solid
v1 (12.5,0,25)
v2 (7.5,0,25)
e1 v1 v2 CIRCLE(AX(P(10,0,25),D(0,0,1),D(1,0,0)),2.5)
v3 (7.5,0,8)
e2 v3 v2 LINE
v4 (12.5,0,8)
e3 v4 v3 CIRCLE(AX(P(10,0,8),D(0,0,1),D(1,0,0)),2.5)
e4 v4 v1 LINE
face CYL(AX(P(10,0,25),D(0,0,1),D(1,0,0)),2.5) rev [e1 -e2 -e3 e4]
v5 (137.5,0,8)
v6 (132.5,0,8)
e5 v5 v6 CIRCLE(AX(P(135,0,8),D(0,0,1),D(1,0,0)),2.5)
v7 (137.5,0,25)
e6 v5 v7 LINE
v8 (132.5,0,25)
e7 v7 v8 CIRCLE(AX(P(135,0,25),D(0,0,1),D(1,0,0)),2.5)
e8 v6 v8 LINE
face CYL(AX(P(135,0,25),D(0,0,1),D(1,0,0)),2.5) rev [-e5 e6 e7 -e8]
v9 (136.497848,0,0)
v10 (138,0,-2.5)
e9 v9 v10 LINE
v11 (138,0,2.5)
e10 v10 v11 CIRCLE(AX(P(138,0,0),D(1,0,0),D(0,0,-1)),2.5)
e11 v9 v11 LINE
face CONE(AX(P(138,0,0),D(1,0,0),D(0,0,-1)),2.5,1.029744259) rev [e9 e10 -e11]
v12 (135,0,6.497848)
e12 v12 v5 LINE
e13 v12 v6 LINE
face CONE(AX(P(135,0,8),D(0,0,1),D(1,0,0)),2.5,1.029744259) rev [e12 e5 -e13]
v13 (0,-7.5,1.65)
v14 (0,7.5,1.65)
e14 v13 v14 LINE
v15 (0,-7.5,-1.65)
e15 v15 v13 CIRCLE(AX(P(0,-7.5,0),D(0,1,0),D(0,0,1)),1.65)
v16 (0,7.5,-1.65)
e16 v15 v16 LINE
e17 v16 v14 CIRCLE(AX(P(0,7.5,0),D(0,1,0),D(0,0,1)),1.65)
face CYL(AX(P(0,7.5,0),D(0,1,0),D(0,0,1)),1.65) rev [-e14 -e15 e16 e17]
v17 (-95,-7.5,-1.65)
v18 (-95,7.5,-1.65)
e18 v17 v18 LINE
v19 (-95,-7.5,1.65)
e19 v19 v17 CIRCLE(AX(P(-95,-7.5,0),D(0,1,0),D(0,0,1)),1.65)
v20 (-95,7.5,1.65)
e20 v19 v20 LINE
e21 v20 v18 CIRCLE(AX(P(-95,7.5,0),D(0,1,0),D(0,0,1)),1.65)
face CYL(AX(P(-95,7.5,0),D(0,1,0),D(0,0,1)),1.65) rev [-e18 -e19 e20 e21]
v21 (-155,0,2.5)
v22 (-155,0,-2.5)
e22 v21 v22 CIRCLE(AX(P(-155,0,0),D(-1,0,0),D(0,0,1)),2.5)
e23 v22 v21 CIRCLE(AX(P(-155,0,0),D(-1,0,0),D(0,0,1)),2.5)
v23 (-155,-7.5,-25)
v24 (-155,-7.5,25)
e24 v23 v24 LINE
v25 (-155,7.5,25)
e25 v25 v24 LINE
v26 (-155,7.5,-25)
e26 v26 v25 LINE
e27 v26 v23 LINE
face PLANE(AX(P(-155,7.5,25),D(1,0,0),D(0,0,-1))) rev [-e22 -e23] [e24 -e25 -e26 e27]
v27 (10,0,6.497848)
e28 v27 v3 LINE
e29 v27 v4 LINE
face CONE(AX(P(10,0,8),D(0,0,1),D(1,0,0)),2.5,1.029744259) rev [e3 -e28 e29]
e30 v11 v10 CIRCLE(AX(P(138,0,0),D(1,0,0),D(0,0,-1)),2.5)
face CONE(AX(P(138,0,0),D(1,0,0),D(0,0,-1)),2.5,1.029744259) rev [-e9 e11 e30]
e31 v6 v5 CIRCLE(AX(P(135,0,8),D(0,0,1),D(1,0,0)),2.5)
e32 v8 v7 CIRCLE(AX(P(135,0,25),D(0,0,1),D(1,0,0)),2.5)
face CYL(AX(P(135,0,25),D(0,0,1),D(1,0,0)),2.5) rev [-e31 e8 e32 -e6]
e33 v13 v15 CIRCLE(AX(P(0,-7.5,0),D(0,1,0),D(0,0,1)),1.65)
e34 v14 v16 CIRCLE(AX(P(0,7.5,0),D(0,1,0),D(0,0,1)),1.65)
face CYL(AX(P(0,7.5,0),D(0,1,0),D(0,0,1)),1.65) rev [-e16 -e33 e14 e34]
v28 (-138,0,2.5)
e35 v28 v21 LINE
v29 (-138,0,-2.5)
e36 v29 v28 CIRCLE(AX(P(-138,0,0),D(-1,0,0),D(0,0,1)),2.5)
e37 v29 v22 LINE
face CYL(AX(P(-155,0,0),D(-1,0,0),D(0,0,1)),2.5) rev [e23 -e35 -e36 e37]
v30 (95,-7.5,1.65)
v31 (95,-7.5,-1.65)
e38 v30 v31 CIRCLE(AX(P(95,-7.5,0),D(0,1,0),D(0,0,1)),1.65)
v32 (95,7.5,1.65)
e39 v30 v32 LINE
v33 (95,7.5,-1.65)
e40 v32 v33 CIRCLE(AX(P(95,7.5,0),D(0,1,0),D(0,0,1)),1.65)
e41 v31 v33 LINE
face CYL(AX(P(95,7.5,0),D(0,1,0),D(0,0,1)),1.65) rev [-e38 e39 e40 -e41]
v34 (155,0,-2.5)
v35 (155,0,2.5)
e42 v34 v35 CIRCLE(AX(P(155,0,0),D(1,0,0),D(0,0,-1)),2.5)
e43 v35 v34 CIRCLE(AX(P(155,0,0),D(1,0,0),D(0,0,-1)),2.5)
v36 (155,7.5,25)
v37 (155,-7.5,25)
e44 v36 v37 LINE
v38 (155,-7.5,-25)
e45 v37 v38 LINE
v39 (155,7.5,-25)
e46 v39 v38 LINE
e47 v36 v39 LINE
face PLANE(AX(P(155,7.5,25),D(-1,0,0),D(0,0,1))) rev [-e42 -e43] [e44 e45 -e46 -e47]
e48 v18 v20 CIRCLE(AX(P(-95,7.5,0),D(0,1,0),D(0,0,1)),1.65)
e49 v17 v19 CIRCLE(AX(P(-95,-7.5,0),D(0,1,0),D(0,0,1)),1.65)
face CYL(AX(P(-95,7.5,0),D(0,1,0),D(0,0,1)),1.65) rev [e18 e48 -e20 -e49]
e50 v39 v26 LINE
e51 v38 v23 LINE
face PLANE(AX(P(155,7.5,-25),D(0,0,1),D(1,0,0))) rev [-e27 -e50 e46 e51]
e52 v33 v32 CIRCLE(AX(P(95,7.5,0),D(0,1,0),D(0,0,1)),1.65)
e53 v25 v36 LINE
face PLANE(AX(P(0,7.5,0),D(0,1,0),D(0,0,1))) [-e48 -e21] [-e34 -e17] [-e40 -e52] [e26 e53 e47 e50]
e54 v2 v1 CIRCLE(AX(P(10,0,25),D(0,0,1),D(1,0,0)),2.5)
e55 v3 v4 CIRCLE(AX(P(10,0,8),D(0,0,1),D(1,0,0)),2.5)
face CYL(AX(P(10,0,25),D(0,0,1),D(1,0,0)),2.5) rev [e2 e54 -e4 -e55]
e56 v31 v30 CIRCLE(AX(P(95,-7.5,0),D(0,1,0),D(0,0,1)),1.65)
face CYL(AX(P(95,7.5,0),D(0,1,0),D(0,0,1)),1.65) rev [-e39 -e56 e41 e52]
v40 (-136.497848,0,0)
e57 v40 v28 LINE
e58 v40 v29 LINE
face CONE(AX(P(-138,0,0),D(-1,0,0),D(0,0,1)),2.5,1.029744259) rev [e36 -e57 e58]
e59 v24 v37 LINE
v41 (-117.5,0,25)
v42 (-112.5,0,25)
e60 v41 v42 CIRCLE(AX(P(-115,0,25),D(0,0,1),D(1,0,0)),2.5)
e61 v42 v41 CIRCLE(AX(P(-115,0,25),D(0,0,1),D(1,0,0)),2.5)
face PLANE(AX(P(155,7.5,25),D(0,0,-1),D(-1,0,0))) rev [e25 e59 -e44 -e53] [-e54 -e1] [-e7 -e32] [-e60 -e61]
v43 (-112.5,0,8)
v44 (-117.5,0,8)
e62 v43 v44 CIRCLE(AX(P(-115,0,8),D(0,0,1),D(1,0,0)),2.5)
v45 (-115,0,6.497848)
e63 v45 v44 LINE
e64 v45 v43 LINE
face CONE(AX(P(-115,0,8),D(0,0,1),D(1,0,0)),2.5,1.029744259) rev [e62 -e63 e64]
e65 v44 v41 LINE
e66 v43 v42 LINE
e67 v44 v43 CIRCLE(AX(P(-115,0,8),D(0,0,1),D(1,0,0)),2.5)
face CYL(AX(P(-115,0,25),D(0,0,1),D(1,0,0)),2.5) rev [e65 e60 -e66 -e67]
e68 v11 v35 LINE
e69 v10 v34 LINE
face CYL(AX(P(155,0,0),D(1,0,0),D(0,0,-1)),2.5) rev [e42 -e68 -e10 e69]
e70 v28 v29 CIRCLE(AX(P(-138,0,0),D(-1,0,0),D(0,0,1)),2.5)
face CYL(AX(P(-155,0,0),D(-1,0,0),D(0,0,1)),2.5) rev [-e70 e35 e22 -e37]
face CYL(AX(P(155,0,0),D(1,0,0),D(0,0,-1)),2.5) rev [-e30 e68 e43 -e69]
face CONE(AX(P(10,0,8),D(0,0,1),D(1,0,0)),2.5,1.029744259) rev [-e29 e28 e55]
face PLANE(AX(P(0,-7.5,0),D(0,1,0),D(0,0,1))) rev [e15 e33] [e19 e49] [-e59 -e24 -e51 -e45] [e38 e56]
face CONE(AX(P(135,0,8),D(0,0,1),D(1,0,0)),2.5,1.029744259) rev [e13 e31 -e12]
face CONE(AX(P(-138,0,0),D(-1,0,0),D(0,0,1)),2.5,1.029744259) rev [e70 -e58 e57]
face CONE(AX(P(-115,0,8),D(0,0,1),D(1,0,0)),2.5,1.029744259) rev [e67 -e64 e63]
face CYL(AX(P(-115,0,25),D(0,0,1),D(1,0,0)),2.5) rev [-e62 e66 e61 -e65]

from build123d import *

# Parameters (mm, degrees)
SKETCH_1_W             = 310
SKETCH_1_H             = 50
EXTRUDE_1_DEPTH        = 7.5
HOLE_WIZARD_M6_1_D     = 5
HOLE_WIZARD_M6_1_DEPTH = 17
HOLE_WIZARD_M6_1_TIP   = 1.502151548
HOLE_WIZARD_M6_2_D     = 5
HOLE_WIZARD_M6_2_DEPTH = 17
HOLE_WIZARD_M6_2_TIP   = 1.502151548
HOLE_WIZARD_M6_3_D     = 5
HOLE_WIZARD_M6_3_DEPTH = 17
HOLE_WIZARD_M6_3_TIP   = 1.502151548
HOLE_WIZARD_M4_1_D     = 3.3


with BuildPart() as part:
    # 草图1 → 凸台-拉伸1 (new, symmetric)
    with BuildSketch(Plane(origin=(0, 0, 0), x_dir=(1, 0, 0), z_dir=(0, 1, 0))):
        Rectangle(SKETCH_1_W, SKETCH_1_H)
    extrude(amount=EXTRUDE_1_DEPTH, both=True)

    # M6 螺纹孔1
    with Locations(Plane.XY.offset(25)):
        with Locations((-115, 0), (10, 0), (135, 0)):
            Hole(HOLE_WIZARD_M6_1_D / 2, depth=HOLE_WIZARD_M6_1_DEPTH)
            with Locations((0, 0, -(HOLE_WIZARD_M6_1_DEPTH + HOLE_WIZARD_M6_1_TIP / 2))):  # 118° drill point
                Cone(0, HOLE_WIZARD_M6_1_D / 2, HOLE_WIZARD_M6_1_TIP, mode=Mode.SUBTRACT)

    # M6 螺纹孔2
    with Locations(Plane(origin=(155, 0, 0), x_dir=(0, 0, -1), z_dir=(1, 0, 0))):
        with Locations((0, 0)):
            Hole(HOLE_WIZARD_M6_2_D / 2, depth=HOLE_WIZARD_M6_2_DEPTH)
            with Locations((0, 0, -(HOLE_WIZARD_M6_2_DEPTH + HOLE_WIZARD_M6_2_TIP / 2))):  # 118° drill point
                Cone(0, HOLE_WIZARD_M6_2_D / 2, HOLE_WIZARD_M6_2_TIP, mode=Mode.SUBTRACT)

    # M6 螺纹孔3
    with Locations(Plane.ZY.offset(155)):
        with Locations((0, 0)):
            Hole(HOLE_WIZARD_M6_3_D / 2, depth=HOLE_WIZARD_M6_3_DEPTH)
            with Locations((0, 0, -(HOLE_WIZARD_M6_3_DEPTH + HOLE_WIZARD_M6_3_TIP / 2))):  # 118° drill point
                Cone(0, HOLE_WIZARD_M6_3_D / 2, HOLE_WIZARD_M6_3_TIP, mode=Mode.SUBTRACT)

    # M4 螺纹孔1 (through all)
    with Locations(Plane(origin=(0, 7.5, 0), x_dir=(1, 0, 0), z_dir=(0, 1, 0))):
        with Locations((-95, 0), (0, 0), (95, 0)):
            Hole(HOLE_WIZARD_M4_1_D / 2)


solid = part.part
